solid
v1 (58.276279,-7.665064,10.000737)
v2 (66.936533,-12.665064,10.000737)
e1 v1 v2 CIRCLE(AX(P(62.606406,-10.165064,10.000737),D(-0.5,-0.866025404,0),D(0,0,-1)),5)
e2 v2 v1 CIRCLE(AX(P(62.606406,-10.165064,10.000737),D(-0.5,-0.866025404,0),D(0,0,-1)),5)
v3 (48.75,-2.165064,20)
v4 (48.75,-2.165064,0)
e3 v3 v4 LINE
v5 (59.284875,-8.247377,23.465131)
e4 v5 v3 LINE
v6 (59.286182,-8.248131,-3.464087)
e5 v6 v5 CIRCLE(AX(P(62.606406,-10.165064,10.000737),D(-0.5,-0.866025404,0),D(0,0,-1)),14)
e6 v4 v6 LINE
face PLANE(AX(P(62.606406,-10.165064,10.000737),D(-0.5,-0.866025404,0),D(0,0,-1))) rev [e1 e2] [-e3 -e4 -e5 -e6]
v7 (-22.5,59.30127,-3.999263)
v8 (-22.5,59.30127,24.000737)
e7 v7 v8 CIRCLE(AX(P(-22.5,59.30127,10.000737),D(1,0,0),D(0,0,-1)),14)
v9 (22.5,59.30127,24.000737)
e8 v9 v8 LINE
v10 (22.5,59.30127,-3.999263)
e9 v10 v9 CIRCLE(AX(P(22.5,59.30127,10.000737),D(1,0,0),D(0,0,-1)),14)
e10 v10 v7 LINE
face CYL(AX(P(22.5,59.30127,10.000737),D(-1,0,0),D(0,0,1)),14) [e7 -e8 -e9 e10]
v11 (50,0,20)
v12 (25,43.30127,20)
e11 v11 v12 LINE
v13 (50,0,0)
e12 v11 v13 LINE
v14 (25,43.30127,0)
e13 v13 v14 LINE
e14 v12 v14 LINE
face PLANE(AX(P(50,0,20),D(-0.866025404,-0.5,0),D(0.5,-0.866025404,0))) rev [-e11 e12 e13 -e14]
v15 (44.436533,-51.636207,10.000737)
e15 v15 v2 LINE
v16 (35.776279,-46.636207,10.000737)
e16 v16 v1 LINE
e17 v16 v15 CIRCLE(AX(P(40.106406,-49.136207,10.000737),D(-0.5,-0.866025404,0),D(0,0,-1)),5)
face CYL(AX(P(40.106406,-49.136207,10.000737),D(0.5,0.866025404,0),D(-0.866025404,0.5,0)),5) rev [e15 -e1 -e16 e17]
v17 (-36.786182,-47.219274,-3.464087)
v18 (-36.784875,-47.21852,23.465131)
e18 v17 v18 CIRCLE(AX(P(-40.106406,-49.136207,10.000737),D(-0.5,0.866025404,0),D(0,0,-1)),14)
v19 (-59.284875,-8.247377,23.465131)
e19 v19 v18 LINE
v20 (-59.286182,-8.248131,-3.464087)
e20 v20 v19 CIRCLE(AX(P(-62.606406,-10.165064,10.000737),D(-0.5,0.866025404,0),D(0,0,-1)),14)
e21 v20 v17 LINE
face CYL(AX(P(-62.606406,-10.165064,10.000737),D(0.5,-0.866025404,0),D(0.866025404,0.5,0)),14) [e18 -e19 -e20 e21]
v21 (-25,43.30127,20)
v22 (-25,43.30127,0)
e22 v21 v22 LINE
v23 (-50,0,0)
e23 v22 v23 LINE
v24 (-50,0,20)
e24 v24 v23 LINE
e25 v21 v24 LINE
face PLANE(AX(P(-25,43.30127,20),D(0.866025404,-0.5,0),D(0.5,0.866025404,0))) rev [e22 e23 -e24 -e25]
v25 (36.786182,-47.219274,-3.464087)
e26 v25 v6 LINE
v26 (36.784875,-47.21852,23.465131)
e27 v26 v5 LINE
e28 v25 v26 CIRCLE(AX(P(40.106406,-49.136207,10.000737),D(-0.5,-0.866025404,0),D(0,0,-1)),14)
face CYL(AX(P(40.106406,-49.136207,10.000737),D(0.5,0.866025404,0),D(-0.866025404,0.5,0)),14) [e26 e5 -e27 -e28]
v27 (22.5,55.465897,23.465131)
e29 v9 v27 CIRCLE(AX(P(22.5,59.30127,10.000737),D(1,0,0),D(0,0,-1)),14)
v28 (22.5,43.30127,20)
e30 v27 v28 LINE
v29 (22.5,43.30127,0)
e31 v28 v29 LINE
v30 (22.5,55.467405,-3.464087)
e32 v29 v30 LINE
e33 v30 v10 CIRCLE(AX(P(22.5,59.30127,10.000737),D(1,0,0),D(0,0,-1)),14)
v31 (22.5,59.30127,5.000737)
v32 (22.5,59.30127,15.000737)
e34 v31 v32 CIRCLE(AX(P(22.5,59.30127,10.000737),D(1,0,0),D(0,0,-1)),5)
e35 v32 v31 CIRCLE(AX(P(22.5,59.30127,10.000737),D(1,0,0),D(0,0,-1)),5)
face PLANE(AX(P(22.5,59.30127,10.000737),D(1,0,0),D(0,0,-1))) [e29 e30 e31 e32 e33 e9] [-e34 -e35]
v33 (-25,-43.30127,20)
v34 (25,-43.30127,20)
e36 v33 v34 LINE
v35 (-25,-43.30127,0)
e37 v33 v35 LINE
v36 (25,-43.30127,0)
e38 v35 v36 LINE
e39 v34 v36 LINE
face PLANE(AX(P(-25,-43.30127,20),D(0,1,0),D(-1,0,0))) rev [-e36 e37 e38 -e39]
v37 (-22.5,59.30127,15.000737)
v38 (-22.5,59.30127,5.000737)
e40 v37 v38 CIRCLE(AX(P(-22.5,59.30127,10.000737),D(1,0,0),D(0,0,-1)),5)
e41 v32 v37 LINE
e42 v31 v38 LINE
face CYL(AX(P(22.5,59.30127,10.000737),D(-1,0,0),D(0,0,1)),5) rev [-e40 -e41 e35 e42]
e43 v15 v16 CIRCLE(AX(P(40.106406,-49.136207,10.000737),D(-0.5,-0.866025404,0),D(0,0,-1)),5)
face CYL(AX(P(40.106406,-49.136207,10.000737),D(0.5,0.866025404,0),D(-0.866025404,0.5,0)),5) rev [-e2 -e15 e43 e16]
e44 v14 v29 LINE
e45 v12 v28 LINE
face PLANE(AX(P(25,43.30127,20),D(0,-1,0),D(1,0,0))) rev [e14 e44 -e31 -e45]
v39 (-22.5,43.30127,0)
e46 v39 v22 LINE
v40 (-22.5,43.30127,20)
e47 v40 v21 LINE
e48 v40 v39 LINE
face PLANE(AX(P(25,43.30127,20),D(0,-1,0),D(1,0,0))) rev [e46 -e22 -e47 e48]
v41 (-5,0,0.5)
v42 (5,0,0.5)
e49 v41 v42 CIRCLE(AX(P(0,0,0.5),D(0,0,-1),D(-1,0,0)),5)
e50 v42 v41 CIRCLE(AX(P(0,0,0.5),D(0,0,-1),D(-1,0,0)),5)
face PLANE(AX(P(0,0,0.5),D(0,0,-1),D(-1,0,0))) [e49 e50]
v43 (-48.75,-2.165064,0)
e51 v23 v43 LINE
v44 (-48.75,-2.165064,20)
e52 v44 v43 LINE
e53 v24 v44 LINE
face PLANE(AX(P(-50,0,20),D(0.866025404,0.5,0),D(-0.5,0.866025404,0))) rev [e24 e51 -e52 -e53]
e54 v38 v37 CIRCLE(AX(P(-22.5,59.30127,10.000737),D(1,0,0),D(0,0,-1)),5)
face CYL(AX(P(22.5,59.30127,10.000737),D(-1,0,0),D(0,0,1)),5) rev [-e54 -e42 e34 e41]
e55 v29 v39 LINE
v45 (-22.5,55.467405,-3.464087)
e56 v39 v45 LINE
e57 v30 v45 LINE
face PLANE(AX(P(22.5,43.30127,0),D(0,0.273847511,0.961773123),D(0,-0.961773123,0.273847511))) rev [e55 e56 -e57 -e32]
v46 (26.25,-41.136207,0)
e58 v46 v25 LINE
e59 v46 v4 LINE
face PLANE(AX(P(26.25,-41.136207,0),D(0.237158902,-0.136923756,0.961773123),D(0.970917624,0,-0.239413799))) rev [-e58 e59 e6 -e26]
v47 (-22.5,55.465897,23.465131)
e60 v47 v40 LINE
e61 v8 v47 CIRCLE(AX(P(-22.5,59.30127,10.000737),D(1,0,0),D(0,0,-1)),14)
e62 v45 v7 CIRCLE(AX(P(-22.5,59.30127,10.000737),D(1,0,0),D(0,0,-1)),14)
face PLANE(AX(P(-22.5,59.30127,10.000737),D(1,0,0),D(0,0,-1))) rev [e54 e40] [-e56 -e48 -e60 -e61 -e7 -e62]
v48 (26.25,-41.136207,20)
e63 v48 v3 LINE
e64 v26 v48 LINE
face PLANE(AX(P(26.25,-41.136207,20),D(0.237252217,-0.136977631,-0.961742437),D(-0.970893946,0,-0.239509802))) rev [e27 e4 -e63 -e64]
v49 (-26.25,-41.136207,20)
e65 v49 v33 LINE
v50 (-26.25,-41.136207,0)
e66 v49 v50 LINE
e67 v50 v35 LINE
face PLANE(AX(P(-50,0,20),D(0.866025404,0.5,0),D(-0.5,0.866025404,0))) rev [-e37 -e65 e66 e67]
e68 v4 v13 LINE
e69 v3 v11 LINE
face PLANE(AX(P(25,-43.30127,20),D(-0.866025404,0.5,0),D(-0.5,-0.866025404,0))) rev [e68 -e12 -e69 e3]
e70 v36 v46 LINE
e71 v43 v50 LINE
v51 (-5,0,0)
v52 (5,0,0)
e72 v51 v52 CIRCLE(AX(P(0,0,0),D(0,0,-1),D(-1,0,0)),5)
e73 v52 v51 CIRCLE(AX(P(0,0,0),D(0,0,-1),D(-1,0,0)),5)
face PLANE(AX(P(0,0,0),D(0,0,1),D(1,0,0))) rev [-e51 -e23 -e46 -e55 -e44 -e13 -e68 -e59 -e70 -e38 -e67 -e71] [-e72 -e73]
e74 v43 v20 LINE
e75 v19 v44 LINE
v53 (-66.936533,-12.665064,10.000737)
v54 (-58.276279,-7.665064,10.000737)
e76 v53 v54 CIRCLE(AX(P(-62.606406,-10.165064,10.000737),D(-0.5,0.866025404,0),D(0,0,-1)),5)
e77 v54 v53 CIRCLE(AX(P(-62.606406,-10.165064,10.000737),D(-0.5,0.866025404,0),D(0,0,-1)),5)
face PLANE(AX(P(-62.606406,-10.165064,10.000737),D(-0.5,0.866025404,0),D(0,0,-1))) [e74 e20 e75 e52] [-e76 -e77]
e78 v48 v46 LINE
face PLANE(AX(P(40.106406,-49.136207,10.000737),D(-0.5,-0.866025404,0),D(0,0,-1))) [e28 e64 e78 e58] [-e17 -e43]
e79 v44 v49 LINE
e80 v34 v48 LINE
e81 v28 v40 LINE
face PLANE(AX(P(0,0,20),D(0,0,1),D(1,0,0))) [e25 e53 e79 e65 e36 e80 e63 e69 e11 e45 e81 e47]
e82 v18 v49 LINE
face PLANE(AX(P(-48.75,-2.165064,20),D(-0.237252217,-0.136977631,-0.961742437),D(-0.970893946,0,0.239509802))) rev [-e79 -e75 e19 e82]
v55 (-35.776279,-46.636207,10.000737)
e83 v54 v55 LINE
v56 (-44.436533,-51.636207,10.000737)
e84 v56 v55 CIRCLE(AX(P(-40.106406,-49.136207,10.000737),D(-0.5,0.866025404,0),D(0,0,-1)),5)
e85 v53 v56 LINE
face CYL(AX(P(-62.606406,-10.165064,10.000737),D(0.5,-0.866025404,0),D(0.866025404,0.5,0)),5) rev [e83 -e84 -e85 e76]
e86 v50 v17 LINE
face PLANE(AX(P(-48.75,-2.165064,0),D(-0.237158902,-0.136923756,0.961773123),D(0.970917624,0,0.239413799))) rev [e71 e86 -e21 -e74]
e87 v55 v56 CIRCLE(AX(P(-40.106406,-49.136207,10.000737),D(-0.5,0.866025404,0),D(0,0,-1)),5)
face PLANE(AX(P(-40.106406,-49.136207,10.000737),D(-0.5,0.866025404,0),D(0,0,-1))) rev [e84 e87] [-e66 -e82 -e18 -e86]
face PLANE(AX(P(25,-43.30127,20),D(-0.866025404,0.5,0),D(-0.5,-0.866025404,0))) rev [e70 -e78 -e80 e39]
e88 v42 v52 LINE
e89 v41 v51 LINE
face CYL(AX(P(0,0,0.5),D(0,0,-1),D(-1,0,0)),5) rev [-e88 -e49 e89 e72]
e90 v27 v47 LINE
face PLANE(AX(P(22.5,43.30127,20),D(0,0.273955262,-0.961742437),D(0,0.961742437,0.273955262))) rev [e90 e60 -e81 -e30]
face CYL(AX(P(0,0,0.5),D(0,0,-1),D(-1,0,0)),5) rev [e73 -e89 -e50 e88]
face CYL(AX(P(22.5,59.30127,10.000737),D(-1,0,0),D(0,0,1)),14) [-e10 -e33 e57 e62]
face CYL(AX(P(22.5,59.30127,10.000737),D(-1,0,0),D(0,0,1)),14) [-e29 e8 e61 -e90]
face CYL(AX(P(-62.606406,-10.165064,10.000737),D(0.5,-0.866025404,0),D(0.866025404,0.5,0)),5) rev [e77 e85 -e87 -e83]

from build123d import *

# Parameters (mm, degrees)
BOSS_EXTRUDE1_DEPTH = 20
SKETCH2_R           = 5
BOSS_EXTRUDE2_DEPTH = 22.5
SKETCH4_R           = 5
CUT_EXTRUDE1_DEPTH  = 0.5
CIRPATTERN1_COUNT   = 3


with BuildPart() as part:
    # Sketch1 → Boss-Extrude1 (new body)
    with BuildSketch(Plane.XY):
        Polygon((50, 0), (25, 43.301270189), (-25, 43.301270189), (-50, 0), (-25, -43.301270189), (25, -43.301270189), align=None)
    extrude(amount=BOSS_EXTRUDE1_DEPTH)

    # Sketch2 → Boss-Extrude2 (add, symmetric)
    with BuildSketch(Plane(origin=(0, 0, 0), x_dir=(0, 0, -1), z_dir=(1, 0, 0))):
        with BuildLine():
            Line((-20, 43.301270189), (-23.46513086, 55.465896517))
            ThreePointArc((-23.46513086, 55.465896517), (-10.001520995, 73.301270167), (3.464086976, 55.467405029))
            Line((3.464086976, 55.467405029), (0, 43.301270189))
            Line((0, 43.301270189), (-20, 43.301270189))
        make_face()
        with Locations(Location((-10.000736748, 59.301270189, 0), (0, 0, 180))):
            Circle(SKETCH2_R, mode=Mode.SUBTRACT)
    boss_extrude2 = extrude(amount=BOSS_EXTRUDE2_DEPTH, both=True)

    # Sketch4 → Cut-Extrude1 (cut)
    with BuildSketch(Plane(origin=(0, 0, 0), x_dir=(-1, 0, 0), z_dir=(0, 0, -1))):
        Circle(SKETCH4_R)
    extrude(amount=-CUT_EXTRUDE1_DEPTH, mode=Mode.SUBTRACT)

    # CirPattern1: Boss-Extrude2 ×3 about axis
    cirpattern1_axis = Axis((0, 0, 0), (0, 0, 1))
    for i in range(1, CIRPATTERN1_COUNT):
        add(boss_extrude2.rotate(cirpattern1_axis, i * 360 / CIRPATTERN1_COUNT))


solid = part.part
